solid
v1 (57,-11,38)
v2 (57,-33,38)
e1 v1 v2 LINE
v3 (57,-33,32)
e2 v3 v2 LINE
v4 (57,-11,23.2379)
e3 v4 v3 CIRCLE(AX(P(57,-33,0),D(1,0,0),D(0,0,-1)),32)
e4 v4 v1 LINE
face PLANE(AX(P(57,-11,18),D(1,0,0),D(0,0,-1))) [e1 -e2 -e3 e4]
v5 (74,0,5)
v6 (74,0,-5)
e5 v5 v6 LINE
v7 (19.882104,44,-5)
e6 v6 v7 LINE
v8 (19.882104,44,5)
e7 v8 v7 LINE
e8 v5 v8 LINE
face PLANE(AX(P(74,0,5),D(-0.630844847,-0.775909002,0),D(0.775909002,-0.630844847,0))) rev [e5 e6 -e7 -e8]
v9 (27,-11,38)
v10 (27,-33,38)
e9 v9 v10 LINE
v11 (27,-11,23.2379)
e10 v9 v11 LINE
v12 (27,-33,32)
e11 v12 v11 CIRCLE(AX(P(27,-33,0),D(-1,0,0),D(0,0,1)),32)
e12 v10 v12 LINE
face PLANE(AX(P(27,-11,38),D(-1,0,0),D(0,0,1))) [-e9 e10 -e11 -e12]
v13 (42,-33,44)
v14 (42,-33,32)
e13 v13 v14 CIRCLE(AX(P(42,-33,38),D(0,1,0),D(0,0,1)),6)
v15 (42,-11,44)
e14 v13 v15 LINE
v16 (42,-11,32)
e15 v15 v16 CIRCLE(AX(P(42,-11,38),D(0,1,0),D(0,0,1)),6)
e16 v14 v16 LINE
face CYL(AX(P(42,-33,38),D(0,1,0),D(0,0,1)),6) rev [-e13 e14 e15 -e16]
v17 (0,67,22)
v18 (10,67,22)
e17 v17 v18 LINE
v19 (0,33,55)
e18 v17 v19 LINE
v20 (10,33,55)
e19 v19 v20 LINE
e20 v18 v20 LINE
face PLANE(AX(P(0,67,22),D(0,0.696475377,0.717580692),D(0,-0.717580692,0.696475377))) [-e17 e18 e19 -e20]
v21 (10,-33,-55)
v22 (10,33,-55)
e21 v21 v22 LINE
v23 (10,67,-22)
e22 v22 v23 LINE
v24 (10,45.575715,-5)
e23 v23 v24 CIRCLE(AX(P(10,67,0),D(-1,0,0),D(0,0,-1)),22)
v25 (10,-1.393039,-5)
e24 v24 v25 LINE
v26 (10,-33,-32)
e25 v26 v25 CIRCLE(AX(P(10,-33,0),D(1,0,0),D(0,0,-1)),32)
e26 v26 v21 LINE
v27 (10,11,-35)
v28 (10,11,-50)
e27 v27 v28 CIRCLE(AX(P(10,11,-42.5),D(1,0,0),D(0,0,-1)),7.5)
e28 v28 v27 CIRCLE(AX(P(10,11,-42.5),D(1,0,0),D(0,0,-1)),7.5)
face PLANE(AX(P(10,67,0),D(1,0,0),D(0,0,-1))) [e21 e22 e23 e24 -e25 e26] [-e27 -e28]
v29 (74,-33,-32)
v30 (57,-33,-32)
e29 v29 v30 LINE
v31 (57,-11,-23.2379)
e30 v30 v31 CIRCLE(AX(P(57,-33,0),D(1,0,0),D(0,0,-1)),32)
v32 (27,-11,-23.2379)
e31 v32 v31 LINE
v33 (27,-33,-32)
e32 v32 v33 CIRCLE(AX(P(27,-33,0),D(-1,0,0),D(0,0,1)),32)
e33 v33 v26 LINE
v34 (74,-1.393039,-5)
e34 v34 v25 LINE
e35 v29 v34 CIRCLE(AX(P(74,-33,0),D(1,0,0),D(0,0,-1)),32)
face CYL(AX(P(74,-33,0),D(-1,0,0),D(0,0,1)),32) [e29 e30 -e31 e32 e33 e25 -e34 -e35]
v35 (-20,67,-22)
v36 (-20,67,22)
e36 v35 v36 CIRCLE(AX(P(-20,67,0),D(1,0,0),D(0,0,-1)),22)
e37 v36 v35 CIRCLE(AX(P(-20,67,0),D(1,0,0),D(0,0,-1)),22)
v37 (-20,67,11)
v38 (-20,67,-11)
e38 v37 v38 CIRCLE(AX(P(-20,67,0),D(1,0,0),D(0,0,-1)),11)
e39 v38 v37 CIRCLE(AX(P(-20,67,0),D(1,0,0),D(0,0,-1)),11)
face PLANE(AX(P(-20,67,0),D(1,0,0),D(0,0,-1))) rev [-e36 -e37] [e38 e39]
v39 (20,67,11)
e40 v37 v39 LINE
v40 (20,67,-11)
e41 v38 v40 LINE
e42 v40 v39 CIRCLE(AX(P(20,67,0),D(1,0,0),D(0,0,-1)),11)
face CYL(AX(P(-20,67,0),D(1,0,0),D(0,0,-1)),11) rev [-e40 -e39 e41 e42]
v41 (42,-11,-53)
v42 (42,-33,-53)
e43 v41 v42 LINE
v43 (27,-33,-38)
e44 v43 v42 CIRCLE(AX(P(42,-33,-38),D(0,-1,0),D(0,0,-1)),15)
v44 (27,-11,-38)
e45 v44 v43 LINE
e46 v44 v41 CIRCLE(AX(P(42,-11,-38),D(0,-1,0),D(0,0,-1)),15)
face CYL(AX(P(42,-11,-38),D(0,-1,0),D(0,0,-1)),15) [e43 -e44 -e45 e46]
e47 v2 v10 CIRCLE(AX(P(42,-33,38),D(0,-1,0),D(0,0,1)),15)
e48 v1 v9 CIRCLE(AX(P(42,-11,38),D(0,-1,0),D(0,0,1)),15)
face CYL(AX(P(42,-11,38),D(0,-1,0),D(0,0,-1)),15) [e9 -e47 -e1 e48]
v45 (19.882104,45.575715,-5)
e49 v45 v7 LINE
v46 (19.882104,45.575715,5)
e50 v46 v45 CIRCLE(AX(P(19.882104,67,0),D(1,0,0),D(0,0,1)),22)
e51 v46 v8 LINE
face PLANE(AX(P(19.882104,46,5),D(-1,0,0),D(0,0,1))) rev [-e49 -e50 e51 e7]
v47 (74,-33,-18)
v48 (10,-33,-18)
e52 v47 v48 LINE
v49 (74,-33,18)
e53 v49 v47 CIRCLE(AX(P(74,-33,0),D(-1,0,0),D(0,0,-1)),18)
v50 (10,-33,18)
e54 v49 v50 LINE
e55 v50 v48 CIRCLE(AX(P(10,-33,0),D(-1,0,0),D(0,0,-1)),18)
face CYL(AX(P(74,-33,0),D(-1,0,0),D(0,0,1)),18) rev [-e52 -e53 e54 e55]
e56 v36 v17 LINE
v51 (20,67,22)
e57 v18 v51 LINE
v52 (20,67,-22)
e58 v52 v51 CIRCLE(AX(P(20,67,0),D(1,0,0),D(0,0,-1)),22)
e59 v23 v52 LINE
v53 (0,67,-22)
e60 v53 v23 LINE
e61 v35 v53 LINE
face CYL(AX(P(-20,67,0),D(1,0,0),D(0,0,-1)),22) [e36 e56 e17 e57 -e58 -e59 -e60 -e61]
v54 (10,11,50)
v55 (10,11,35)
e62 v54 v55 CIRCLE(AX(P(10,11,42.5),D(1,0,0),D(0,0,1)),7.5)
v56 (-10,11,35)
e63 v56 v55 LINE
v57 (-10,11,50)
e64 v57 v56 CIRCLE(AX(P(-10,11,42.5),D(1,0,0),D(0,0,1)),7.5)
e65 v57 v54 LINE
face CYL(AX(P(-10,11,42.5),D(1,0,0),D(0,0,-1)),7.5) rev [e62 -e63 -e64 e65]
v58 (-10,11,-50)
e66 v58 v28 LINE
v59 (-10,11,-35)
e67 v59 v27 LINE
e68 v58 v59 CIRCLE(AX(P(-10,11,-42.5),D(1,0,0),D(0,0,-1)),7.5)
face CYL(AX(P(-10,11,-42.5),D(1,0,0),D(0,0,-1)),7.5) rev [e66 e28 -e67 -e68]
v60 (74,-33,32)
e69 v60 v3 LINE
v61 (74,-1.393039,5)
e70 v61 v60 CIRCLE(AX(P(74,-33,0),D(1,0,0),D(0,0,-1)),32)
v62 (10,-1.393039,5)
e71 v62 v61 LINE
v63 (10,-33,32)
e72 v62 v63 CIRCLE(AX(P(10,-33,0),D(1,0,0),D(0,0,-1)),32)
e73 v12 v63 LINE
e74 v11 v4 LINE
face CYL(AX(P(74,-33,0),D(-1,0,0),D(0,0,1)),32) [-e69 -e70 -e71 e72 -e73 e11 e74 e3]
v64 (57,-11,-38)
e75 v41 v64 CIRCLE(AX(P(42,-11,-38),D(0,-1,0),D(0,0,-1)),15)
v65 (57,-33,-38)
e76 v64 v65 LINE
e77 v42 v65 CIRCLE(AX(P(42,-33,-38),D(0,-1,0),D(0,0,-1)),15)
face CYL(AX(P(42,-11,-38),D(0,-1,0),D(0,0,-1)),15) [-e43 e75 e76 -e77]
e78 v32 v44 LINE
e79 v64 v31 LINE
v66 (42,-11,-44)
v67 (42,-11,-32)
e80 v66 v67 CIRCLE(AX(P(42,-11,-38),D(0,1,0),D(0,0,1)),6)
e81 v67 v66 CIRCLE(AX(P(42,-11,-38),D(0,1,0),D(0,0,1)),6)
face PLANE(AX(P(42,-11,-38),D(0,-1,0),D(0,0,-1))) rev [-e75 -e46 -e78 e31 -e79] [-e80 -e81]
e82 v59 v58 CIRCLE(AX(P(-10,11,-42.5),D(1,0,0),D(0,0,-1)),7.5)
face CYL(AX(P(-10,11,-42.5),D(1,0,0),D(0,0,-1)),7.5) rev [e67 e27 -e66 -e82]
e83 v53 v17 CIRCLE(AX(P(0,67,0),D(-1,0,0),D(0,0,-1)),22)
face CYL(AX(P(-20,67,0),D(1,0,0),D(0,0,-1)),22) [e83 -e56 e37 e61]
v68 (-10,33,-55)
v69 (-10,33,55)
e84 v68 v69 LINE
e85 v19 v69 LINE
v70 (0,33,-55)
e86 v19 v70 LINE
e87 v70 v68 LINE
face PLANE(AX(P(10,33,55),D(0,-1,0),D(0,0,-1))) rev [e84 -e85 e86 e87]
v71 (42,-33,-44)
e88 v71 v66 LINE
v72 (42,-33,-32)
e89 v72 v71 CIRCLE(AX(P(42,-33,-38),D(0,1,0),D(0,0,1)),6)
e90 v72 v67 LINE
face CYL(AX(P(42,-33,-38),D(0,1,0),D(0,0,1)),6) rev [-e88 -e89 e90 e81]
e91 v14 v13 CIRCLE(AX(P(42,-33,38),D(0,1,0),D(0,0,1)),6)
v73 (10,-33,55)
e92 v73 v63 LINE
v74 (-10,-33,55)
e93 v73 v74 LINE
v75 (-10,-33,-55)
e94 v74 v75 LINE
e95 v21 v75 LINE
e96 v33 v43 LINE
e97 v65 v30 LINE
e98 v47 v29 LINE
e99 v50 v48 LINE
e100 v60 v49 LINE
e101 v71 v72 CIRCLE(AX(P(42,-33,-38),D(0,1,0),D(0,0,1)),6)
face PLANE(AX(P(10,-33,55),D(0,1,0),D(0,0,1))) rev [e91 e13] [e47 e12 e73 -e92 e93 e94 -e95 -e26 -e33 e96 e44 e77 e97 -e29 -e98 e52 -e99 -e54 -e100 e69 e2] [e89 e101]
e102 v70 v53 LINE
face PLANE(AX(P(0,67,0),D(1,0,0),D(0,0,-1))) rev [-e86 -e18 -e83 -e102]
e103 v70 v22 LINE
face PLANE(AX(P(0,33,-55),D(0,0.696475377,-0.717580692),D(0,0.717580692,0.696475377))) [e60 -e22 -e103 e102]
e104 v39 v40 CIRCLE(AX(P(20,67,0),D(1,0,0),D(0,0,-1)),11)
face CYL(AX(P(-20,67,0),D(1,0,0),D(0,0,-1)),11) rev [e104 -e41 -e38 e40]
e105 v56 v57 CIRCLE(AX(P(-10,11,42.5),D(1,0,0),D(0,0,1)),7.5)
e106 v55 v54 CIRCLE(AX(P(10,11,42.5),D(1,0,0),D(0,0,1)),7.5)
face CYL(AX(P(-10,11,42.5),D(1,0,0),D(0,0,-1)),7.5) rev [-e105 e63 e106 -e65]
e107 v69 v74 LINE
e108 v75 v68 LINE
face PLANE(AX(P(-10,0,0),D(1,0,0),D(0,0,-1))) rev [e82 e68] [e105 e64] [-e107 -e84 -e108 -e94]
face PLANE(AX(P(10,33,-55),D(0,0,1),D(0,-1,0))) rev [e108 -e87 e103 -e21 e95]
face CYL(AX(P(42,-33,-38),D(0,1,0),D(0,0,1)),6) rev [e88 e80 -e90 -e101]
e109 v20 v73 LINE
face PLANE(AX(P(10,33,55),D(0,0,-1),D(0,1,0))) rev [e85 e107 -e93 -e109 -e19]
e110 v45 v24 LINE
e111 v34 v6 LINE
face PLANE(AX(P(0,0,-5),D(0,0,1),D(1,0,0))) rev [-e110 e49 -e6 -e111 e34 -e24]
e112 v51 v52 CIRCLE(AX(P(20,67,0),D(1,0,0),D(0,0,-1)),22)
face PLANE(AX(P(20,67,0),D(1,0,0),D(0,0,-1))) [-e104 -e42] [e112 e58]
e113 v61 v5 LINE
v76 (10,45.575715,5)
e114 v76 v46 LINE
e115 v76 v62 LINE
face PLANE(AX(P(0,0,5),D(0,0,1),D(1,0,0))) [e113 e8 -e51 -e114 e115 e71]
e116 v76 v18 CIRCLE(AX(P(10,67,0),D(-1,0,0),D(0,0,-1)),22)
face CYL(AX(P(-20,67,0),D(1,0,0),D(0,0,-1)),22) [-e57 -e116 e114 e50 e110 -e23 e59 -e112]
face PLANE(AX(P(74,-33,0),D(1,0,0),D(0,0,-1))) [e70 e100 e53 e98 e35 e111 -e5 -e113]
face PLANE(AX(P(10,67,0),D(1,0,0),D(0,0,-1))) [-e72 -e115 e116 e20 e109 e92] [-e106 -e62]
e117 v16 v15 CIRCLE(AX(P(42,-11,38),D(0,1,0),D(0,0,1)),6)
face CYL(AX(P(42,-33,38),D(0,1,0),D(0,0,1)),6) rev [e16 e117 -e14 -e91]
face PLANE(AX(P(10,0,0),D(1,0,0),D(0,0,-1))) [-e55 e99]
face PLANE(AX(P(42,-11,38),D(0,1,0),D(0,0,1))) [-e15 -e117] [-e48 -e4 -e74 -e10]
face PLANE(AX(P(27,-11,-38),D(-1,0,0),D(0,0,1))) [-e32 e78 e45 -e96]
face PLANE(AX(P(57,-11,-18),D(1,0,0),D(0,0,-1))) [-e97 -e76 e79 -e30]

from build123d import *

# Parameters (mm, degrees)
BACK_PLATE_SKETCH_W    = 110
BACK_PLATE_SKETCH_H    = 66
BACK_PLATE_DEPTH       = 10
TOP_BOSS_44_DEPTH      = 20
TOP_BOSS_44_DEPTH_BACK = 20
TOP_BOSS_SKETCH_R      = 22
TOP_BOSS_SKETCH_R_2    = 11
PLATE_CUT_SKETCH_R     = 7.5
PLATE_CUT_DEPTH        = 20
BASE_BLOCK_DEPTH       = 64
BEARING_SADDLE_DEPTH   = 22
EAR_HOLES_SKETCH_R     = 6
EAR_HOLES_12_DEPTH     = 22
RIB_DEPTH              = 10
SIDE_PLATE_DEPTH       = 5
PAD_1_SKETCH_W         = 9.88210357
PAD_1_SKETCH_H         = 10
PAD_1_DEPTH            = 2
PAD_2_SKETCH_W         = 64
PAD_2_SKETCH_H         = 10
PAD_2_DEPTH            = 2


with BuildPart() as part:
    # Back Plate Sketch → Back Plate (new, symmetric)
    with BuildSketch(Plane(origin=(0, 0, 0), x_dir=(0, 0, -1), z_dir=(1, 0, 0))):
        Rectangle(BACK_PLATE_SKETCH_W, BACK_PLATE_SKETCH_H)
    extrude(amount=BACK_PLATE_DEPTH, both=True)

    # Plate Cut Sketch → Plate Cut (cut)
    with BuildSketch(Plane(origin=(10, 0, 0), x_dir=(0, 0, -1), z_dir=(1, 0, 0))):
        with Locations((42.5, 11)):
            Circle(PLATE_CUT_SKETCH_R)
        with Locations(Location((-42.5, 11, 0), (0, 0, 180))):
            Circle(PLATE_CUT_SKETCH_R)
    extrude(amount=-PLATE_CUT_DEPTH, mode=Mode.SUBTRACT)

    # Base Block Sketch → Base Block (add)
    with BuildSketch(Plane(origin=(10, 0, 0), x_dir=(0, 0, -1), z_dir=(1, 0, 0))):
        with BuildLine():
            Line((-32, -33), (-18, -33))
            ThreePointArc((-18, -33), (0, -15), (18, -33))
            Line((18, -33), (32, -33))
            ThreePointArc((32, -33), (0, -1), (-32, -33))
        make_face()
    extrude(amount=BASE_BLOCK_DEPTH)

    # Bearing Saddle Sketch → Bearing Saddle (add)
    with BuildSketch(Plane.XZ.offset(33)):
        with BuildLine():
            Line((27, 38), (27, 18))
            Line((27, 18), (57, 18))
            Line((57, 18), (57, 38))
            ThreePointArc((57, 38), (42, 53), (27, 38))
        make_face()
        with BuildLine():
            Line((27, -38), (27, -18))
            Line((27, -18), (57, -18))
            Line((57, -18), (57, -38))
            ThreePointArc((57, -38), (42, -53), (27, -38))
        make_face()
    extrude(amount=-BEARING_SADDLE_DEPTH)

    # Ear Holes Sketch → Ear Holes Ø12 (cut)
    with BuildSketch(Plane(origin=(0, -11, 0), x_dir=(1, 0, 0), z_dir=(0, 1, 0))):
        with Locations(Location((42, 38, 0), (0, 0, 270))):
            Circle(EAR_HOLES_SKETCH_R)
        with Locations(Location((42, -38, 0), (0, 0, 270))):
            Circle(EAR_HOLES_SKETCH_R)
    extrude(amount=-EAR_HOLES_12_DEPTH, mode=Mode.SUBTRACT)



with BuildPart() as body_2:
    # Top Boss Sketch → Top Boss Ø44 (new, two sides: drawn at the far end of the back side and taken through both)
    with BuildSketch(Plane(origin=(0, 0, 0), x_dir=(0, 0, -1), z_dir=(1, 0, 0)).offset(-TOP_BOSS_44_DEPTH_BACK)):
        with Locations((0, 67)):
            Circle(TOP_BOSS_SKETCH_R)
        with Locations((0, 67)):
            Circle(TOP_BOSS_SKETCH_R_2, mode=Mode.SUBTRACT)
    extrude(amount=TOP_BOSS_44_DEPTH + TOP_BOSS_44_DEPTH_BACK)


with BuildPart() as part_1:
    add(part.part)

    add(body_2.part)  # Rib merges body 2
    # Rib Sketch → Rib (add)
    with BuildSketch(Plane(origin=(10, 0, 0), x_dir=(0, 0, -1), z_dir=(1, 0, 0))):
        with BuildLine():
            Line((-22, 67), (-55, 33))
            Line((-55, 33), (55, 33))
            Line((55, 33), (22, 67))
            ThreePointArc((22, 67), (0, 45), (-22, 67))
        make_face()
    extrude(amount=-RIB_DEPTH)

    # Side Plate Sketch → Side Plate (add, symmetric)
    with BuildSketch(Plane.XY):
        Polygon((10, 44), (19.88210357, 44), (74, 0), (10, 0), align=None)
    extrude(amount=SIDE_PLATE_DEPTH, both=True)

    # Pad 1 Sketch → Pad 1 (add)
    with BuildSketch(Plane(origin=(0, 44, 0), x_dir=(1, 0, 0), z_dir=(0, 1, 0))):
        with Locations((14.941051785, 0)):
            Rectangle(PAD_1_SKETCH_W, PAD_1_SKETCH_H)
    extrude(amount=PAD_1_DEPTH)

    # Pad 2 Sketch → Pad 2 (add)
    with BuildSketch(Plane.XZ):
        with Locations((42, 0)):
            Rectangle(PAD_2_SKETCH_W, PAD_2_SKETCH_H)
    extrude(amount=PAD_2_DEPTH)


solid = part_1.part
